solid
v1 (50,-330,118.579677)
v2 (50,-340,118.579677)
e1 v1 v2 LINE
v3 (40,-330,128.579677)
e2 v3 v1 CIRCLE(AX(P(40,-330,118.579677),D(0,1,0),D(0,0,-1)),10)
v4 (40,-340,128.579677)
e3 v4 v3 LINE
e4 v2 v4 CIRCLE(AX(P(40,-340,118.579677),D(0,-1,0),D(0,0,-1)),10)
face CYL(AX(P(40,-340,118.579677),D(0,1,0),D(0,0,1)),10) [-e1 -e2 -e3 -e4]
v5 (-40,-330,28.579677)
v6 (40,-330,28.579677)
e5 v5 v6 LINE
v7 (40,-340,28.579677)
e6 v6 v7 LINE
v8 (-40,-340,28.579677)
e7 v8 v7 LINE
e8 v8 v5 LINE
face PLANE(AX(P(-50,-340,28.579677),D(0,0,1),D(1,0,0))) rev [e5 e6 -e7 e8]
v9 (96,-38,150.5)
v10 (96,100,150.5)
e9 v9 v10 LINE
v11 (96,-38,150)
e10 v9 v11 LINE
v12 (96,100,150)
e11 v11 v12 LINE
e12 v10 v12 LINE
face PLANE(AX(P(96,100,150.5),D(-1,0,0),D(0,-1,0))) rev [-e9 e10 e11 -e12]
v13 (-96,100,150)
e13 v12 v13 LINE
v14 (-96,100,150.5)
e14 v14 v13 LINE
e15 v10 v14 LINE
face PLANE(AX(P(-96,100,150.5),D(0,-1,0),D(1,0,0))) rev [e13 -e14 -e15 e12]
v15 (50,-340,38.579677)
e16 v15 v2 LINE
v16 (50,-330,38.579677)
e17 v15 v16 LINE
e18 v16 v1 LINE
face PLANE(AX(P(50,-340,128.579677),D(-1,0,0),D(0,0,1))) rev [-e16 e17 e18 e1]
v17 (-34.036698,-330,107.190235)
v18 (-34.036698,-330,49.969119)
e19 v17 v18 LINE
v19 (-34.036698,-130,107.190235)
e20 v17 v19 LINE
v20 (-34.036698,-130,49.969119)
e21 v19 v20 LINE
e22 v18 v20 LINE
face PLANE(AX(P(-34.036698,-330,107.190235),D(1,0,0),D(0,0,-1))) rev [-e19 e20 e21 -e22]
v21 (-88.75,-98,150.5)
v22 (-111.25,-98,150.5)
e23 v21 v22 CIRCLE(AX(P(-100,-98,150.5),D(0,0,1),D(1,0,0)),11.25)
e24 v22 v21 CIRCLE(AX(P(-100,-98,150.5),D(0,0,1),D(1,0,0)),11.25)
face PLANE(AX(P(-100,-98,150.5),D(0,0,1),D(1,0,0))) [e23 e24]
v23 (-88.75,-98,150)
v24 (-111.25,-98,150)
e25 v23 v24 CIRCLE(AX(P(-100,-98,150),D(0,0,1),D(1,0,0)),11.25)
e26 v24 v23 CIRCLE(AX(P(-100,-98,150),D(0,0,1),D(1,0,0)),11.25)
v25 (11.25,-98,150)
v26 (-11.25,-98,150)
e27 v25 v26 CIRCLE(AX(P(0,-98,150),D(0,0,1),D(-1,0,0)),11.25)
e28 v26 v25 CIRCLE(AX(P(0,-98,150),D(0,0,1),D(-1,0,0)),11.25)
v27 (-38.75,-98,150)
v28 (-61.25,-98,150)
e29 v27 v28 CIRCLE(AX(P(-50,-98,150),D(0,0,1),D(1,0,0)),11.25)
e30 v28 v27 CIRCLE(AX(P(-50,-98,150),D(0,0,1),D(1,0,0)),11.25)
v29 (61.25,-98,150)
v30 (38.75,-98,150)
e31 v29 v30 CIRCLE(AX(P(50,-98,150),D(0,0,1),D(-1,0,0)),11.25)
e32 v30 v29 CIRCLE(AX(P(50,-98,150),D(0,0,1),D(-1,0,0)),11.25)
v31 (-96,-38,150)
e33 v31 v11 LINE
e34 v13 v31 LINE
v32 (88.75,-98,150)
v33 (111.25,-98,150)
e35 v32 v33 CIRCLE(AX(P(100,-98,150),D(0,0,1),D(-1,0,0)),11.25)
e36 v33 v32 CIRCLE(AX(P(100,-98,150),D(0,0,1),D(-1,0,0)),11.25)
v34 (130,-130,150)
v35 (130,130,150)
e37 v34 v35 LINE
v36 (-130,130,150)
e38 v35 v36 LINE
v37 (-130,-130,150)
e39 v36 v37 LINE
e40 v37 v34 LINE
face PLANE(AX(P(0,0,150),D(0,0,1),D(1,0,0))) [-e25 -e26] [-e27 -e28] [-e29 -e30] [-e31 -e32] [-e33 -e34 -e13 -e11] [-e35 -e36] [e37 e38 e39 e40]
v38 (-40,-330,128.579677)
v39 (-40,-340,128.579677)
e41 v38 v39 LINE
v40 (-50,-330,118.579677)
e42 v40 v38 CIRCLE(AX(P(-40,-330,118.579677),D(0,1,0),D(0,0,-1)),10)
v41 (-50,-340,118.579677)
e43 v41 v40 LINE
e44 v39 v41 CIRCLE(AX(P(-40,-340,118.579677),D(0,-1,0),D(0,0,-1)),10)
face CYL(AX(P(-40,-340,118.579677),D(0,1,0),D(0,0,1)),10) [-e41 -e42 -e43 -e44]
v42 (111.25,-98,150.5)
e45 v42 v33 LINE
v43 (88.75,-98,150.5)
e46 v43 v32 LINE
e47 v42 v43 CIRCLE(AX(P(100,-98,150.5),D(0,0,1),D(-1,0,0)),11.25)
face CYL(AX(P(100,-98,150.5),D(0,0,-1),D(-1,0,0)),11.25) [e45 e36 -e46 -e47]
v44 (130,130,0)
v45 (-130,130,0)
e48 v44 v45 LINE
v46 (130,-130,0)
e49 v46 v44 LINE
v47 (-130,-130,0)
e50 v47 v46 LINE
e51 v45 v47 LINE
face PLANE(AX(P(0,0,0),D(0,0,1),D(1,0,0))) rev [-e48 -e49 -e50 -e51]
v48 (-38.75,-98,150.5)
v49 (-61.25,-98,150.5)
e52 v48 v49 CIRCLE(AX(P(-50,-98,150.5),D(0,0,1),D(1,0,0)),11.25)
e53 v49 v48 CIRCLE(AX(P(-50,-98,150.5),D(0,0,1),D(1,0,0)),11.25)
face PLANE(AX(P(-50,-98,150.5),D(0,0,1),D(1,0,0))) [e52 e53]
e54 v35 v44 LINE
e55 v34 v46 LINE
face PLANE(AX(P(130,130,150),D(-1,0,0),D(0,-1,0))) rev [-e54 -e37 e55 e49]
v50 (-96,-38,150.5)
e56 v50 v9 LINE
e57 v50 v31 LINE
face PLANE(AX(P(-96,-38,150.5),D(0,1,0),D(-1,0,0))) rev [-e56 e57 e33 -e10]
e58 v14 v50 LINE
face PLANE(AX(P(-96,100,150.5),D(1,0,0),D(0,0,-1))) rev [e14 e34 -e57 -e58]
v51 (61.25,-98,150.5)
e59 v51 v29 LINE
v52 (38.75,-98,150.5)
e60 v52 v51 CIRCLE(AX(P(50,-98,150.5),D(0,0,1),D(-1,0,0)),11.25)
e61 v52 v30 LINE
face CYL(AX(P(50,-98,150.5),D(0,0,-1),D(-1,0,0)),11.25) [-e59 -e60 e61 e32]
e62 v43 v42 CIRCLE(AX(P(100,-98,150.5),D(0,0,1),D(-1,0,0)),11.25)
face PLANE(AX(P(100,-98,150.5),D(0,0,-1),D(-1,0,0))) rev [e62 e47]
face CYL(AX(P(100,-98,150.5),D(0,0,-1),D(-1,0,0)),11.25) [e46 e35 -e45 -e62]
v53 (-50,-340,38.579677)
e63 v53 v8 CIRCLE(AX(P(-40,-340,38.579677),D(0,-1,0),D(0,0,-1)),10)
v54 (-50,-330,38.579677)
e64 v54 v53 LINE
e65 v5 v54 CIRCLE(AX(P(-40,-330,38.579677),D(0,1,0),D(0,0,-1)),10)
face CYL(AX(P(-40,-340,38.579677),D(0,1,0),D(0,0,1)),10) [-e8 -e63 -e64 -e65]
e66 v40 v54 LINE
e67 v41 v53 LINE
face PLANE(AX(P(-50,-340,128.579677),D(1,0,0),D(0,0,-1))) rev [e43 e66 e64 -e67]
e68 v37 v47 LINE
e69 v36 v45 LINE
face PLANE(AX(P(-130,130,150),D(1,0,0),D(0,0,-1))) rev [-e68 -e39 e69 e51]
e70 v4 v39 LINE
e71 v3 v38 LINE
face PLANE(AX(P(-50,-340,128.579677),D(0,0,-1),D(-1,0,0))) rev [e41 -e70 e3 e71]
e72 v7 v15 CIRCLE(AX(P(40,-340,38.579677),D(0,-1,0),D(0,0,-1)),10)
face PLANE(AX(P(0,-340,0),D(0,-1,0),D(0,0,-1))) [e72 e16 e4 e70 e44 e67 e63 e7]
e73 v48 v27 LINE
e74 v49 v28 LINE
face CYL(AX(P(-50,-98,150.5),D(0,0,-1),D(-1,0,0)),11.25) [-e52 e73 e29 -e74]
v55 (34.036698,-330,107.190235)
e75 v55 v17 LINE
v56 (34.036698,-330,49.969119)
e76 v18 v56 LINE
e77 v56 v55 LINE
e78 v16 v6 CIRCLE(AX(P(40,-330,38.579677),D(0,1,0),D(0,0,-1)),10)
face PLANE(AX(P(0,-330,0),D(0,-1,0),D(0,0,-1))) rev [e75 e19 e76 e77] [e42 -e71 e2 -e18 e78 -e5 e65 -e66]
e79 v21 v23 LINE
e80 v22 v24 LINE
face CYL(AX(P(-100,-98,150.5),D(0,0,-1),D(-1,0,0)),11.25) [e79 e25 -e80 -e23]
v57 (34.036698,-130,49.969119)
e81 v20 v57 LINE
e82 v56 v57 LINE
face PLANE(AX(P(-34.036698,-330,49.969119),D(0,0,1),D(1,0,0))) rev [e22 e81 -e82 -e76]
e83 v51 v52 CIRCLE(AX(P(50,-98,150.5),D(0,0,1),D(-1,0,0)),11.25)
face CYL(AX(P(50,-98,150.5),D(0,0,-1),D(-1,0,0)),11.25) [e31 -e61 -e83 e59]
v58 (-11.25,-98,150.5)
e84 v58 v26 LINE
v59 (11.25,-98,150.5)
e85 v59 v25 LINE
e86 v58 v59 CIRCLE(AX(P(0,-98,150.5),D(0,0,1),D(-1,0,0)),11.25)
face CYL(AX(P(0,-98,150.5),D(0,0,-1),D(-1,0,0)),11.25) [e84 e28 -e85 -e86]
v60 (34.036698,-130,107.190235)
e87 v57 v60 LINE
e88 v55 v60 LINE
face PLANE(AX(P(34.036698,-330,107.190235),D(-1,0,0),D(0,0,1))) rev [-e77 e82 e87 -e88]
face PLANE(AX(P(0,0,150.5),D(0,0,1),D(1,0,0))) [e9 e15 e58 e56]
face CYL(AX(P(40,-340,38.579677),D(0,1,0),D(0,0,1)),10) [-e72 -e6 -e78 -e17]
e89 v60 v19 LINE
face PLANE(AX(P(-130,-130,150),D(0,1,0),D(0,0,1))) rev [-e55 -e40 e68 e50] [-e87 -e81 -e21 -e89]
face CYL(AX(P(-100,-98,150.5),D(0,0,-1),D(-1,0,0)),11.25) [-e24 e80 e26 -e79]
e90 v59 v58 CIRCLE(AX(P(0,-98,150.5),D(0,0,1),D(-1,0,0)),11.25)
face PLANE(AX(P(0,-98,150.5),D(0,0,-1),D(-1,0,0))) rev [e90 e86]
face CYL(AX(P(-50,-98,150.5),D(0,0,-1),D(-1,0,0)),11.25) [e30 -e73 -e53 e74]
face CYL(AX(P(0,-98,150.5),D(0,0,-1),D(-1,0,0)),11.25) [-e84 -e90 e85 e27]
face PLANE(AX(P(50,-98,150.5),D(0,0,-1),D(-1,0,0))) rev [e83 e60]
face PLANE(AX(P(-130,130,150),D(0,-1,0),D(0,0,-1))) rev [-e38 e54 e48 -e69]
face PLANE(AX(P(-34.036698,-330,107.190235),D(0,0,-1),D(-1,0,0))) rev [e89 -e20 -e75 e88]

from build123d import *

# Parameters (mm, degrees)
SKETCH1_W           = 260
SKETCH1_H           = 260
BOSS_EXTRUDE1_DEPTH = 150
SKETCH2_R           = 11.25
SKETCH2_W           = 192
SKETCH2_H           = 138
BOSS_EXTRUDE2_DEPTH = 0.5
SKETCH3_W           = 68.073396254
SKETCH3_H           = 57.221115693
BOSS_EXTRUDE3_DEPTH = 200
SKETCH4_W           = 100
SKETCH4_H           = 100
BOSS_EXTRUDE4_DEPTH = 10
FILLET1_R           = 10


with BuildPart() as part:
    # Sketch1 → Boss-Extrude1 (new body)
    with BuildSketch(Plane.XY):
        Rectangle(SKETCH1_W, SKETCH1_H)
    extrude(amount=BOSS_EXTRUDE1_DEPTH)

    # Sketch2 → Boss-Extrude2 (add)
    with BuildSketch(Plane.XY.offset(150)):
        with Locations((-100, -98)):
            Circle(SKETCH2_R)
        with Locations((-50, -98)):
            Circle(SKETCH2_R)
        with Locations(Location((50, -98, 0), (0, 0, 180))):
            Circle(SKETCH2_R)
        with Locations(Location((100, -98, 0), (0, 0, 180))):
            Circle(SKETCH2_R)
        with Locations(Location((0, -98, 0), (0, 0, 180))):
            Circle(SKETCH2_R)
        with Locations((0, 31)):
            Rectangle(SKETCH2_W, SKETCH2_H)
    extrude(amount=BOSS_EXTRUDE2_DEPTH)

    # Sketch3 → Boss-Extrude3 (add)
    with BuildSketch(Plane.XZ.offset(130)):
        with Locations((0, 78.579676991)):
            Rectangle(SKETCH3_W, SKETCH3_H)
    extrude(amount=BOSS_EXTRUDE3_DEPTH)

    # Sketch4 → Boss-Extrude4 (add)
    with BuildSketch(Plane.XZ.offset(330)):
        with Locations((0, 78.579676991)):
            Rectangle(SKETCH4_W, SKETCH4_H)
    extrude(amount=BOSS_EXTRUDE4_DEPTH)

    # Fillet1
    fillet1_edges = [part.edges().sort_by_distance(p)[0] for p in [
        (50, -335, 28.579676991),
        (50, -335, 128.579676991),
        (-50, -335, 128.579676991),
        (-50, -335, 28.579676991),
    ]]
    fillet(fillet1_edges, radius=FILLET1_R)


solid = part.part
